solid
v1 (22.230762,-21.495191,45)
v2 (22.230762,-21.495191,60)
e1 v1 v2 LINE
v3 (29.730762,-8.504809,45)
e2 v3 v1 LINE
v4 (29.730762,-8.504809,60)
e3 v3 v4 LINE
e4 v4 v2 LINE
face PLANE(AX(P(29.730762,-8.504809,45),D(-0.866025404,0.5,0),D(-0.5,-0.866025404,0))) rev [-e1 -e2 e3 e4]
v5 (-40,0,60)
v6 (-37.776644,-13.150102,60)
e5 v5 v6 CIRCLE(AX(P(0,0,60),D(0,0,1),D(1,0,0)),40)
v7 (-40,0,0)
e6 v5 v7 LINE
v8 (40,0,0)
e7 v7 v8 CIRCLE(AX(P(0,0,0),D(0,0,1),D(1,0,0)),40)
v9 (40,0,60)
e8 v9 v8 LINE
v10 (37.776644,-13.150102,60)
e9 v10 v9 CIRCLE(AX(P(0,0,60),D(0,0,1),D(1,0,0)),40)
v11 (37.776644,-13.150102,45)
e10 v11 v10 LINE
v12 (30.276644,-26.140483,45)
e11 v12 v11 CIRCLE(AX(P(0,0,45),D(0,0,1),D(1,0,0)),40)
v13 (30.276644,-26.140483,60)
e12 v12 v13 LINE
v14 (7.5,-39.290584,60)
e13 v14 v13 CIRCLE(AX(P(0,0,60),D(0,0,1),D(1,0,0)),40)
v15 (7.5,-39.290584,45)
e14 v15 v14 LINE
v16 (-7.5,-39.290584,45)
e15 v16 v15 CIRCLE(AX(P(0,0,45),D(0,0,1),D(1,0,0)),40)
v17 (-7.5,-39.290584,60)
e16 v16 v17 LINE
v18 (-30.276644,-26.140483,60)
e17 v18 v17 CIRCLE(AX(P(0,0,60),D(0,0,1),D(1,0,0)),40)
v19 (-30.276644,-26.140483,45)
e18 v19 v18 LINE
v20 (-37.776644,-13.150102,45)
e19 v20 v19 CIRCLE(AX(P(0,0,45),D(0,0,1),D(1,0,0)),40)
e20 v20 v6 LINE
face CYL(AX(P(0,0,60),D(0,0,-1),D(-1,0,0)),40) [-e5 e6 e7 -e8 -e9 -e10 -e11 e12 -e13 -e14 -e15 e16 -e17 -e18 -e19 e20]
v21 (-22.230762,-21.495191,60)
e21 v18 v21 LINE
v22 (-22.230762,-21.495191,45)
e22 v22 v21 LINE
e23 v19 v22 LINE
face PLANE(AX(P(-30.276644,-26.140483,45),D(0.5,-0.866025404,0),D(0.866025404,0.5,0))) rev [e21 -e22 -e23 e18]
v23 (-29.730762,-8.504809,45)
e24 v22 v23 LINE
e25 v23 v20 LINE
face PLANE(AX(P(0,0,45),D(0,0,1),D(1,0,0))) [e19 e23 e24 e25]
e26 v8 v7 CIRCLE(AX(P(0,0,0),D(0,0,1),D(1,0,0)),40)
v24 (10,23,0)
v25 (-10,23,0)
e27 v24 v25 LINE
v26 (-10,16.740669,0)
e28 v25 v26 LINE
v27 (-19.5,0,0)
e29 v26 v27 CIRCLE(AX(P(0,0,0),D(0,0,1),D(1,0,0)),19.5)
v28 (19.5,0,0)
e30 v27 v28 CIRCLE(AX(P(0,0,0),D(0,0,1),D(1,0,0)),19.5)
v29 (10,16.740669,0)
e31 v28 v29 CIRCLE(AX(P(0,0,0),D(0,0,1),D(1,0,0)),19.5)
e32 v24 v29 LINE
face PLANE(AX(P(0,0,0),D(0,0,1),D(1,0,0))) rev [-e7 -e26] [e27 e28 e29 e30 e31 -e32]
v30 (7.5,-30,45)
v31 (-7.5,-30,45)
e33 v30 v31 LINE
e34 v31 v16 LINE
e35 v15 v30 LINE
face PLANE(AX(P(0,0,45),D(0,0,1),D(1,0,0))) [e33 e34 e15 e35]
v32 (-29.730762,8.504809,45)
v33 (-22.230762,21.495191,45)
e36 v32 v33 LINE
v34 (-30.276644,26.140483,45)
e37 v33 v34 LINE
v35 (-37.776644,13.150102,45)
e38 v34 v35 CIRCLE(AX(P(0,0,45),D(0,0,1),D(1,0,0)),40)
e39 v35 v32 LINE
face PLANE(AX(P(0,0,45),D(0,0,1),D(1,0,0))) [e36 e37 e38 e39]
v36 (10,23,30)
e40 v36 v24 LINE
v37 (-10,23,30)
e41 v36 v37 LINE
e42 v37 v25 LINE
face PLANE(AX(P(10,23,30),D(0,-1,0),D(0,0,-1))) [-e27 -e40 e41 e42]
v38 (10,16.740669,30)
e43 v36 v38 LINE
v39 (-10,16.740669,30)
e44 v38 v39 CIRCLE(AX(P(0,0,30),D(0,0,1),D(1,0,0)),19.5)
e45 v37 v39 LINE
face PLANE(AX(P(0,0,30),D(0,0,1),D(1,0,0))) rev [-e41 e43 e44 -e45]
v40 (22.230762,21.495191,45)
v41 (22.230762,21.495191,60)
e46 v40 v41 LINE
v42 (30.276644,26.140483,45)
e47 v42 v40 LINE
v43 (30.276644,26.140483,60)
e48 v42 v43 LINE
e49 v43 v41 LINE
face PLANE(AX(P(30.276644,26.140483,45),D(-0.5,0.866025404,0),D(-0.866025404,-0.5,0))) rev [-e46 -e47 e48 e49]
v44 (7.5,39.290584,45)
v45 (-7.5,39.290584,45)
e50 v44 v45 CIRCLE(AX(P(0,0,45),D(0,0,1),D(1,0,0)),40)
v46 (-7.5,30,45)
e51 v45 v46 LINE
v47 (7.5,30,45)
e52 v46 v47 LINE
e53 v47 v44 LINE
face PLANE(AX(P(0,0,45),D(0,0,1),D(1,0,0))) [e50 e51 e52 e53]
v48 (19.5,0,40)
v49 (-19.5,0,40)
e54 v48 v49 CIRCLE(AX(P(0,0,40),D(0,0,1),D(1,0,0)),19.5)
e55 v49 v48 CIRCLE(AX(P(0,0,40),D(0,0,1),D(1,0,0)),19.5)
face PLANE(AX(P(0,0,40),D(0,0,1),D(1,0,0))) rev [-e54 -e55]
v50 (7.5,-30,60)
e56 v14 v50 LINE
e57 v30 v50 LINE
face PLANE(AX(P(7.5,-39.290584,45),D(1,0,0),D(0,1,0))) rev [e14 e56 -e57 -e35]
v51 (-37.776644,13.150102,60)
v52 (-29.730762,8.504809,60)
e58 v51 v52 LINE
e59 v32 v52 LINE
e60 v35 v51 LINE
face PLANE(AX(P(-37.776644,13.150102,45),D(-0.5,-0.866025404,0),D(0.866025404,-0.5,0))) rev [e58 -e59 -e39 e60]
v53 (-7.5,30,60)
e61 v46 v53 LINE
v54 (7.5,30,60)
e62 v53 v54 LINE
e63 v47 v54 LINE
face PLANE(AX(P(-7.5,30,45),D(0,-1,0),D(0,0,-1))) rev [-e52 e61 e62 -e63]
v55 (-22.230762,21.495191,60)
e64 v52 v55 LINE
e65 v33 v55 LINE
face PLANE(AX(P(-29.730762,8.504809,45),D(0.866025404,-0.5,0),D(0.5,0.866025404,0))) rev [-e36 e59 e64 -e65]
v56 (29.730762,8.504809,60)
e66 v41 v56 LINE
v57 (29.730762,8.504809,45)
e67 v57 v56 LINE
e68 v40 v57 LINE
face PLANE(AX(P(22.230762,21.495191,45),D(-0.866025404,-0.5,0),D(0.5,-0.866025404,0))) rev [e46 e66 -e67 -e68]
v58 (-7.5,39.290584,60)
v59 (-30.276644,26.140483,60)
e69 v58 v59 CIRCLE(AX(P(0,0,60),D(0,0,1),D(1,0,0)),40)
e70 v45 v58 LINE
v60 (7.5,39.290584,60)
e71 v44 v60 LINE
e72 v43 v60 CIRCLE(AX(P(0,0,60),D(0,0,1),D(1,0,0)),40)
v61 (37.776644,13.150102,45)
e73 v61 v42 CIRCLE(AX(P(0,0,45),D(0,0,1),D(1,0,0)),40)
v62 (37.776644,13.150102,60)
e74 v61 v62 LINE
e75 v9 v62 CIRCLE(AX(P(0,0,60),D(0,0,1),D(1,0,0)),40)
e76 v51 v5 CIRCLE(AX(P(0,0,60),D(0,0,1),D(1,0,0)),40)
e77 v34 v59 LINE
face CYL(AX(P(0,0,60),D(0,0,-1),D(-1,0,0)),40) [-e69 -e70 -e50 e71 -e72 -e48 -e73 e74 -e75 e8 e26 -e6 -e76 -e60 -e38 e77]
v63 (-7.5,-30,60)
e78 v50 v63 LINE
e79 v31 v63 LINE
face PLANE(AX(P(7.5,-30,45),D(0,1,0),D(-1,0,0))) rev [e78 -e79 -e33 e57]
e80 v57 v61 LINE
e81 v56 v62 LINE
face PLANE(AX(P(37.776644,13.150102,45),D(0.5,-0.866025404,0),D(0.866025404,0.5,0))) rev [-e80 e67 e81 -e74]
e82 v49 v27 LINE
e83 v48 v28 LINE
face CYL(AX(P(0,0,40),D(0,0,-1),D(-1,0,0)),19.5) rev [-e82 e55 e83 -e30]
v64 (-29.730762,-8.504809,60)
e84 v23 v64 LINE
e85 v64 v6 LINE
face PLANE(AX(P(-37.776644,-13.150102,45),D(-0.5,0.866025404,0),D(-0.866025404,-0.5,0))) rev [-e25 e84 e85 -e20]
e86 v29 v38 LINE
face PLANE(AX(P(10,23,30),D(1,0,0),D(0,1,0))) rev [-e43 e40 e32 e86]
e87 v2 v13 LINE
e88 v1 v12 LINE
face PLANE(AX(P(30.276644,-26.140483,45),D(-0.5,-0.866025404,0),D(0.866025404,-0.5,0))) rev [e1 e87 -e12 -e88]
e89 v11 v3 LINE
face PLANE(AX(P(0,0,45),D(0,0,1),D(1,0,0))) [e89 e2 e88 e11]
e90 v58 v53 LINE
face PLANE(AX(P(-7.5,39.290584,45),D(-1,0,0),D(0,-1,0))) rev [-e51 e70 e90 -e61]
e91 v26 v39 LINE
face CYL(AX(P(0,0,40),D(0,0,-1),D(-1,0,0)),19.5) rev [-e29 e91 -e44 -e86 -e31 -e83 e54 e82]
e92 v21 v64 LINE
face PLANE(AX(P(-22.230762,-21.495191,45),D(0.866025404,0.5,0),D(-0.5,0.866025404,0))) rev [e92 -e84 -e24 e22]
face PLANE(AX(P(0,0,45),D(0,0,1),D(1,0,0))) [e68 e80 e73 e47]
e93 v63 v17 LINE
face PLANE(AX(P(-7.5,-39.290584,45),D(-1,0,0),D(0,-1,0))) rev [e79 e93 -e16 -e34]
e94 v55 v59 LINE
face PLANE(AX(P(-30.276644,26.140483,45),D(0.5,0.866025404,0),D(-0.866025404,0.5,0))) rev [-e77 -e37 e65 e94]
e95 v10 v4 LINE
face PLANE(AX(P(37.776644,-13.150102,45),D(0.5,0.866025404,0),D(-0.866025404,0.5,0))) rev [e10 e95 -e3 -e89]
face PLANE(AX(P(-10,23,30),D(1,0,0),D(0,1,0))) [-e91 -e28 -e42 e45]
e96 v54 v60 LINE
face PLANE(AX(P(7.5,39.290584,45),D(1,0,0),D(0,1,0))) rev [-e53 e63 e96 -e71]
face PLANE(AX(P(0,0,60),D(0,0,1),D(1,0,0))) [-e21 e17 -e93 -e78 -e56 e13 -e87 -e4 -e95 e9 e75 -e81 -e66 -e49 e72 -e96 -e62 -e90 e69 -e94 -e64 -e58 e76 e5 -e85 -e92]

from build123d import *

# Parameters (mm, degrees)
SKETCH_2_R          = 40
EXTRUDE_1_DEPTH     = 60
SKETCH_1_R          = 19.5
CUT_EXTRUDE_1_DEPTH = 40
CUT_EXTRUDE_START   = -15
CUT_EXTRUDE_2_DEPTH = 15
SKETCH_4_W          = 20
SKETCH_4_H          = 7.082368082
CUT_EXTRUDE_3_DEPTH = 30


with BuildPart() as part:
    # 草图2 → 凸台-拉伸1 (new body)
    with BuildSketch(Plane.XY):
        Circle(SKETCH_2_R)
    extrude(amount=EXTRUDE_1_DEPTH)

    # 草图1 → 切除-拉伸1 (cut)
    with BuildSketch(Plane.XY):
        Circle(SKETCH_1_R)
    extrude(amount=CUT_EXTRUDE_1_DEPTH, mode=Mode.SUBTRACT)

    # 草图3 → 切除-拉伸2 (cut)
    with BuildSketch(Plane.XY.offset(60).offset(CUT_EXTRUDE_START)):
        with BuildLine():
            Line((22.230762114, 21.495190528), (29.730762114, 8.504809472))
            Line((29.730762114, 8.504809472), (37.776643972, 13.150101528))
            ThreePointArc((37.776643972, 13.150101528), (34.641016151, 20), (30.276643972, 26.140482585))
            Line((30.276643972, 26.140482585), (22.230762114, 21.495190528))
        make_face()
        with BuildLine():
            Line((-7.5, 39.290584114), (-7.5, 30))
            Line((-7.5, 30), (7.5, 30))
            Line((7.5, 30), (7.5, 39.290584114))
            ThreePointArc((7.5, 39.290584114), (0, 40), (-7.5, 39.290584114))
        make_face()
        with BuildLine():
            Line((29.730762114, -8.504809472), (22.230762114, -21.495190528))
            Line((22.230762114, -21.495190528), (30.276643972, -26.140482585))
            ThreePointArc((30.276643972, -26.140482585), (34.641016151, -20), (37.776643972, -13.150101528))
            Line((37.776643972, -13.150101528), (29.730762114, -8.504809472))
        make_face()
        with BuildLine():
            Line((7.5, -30), (-7.5, -30))
            Line((-7.5, -30), (-7.5, -39.290584114))
            ThreePointArc((-7.5, -39.290584114), (0, -40), (7.5, -39.290584114))
            Line((7.5, -39.290584114), (7.5, -30))
        make_face()
        with BuildLine():
            Line((-22.230762114, -21.495190528), (-29.730762114, -8.504809472))
            Line((-29.730762114, -8.504809472), (-37.776643972, -13.150101528))
            ThreePointArc((-37.776643972, -13.150101528), (-34.641016151, -20), (-30.276643972, -26.140482585))
            Line((-30.276643972, -26.140482585), (-22.230762114, -21.495190528))
        make_face()
        with BuildLine():
            Line((-29.730762114, 8.504809472), (-22.230762114, 21.495190528))
            Line((-22.230762114, 21.495190528), (-30.276643972, 26.140482585))
            ThreePointArc((-30.276643972, 26.140482585), (-34.641016151, 20), (-37.776643972, 13.150101528))
            Line((-37.776643972, 13.150101528), (-29.730762114, 8.504809472))
        make_face()
    extrude(amount=CUT_EXTRUDE_2_DEPTH, mode=Mode.SUBTRACT)

    # 草图4 → 切除-拉伸3 (cut)
    with BuildSketch(Plane(origin=(0, 0, 0), x_dir=(-1, 0, 0), z_dir=(0, 0, -1))):
        with Locations((0, 19.458815959)):
            Rectangle(SKETCH_4_W, SKETCH_4_H)
    extrude(amount=-CUT_EXTRUDE_3_DEPTH, mode=Mode.SUBTRACT)


solid = part.part
